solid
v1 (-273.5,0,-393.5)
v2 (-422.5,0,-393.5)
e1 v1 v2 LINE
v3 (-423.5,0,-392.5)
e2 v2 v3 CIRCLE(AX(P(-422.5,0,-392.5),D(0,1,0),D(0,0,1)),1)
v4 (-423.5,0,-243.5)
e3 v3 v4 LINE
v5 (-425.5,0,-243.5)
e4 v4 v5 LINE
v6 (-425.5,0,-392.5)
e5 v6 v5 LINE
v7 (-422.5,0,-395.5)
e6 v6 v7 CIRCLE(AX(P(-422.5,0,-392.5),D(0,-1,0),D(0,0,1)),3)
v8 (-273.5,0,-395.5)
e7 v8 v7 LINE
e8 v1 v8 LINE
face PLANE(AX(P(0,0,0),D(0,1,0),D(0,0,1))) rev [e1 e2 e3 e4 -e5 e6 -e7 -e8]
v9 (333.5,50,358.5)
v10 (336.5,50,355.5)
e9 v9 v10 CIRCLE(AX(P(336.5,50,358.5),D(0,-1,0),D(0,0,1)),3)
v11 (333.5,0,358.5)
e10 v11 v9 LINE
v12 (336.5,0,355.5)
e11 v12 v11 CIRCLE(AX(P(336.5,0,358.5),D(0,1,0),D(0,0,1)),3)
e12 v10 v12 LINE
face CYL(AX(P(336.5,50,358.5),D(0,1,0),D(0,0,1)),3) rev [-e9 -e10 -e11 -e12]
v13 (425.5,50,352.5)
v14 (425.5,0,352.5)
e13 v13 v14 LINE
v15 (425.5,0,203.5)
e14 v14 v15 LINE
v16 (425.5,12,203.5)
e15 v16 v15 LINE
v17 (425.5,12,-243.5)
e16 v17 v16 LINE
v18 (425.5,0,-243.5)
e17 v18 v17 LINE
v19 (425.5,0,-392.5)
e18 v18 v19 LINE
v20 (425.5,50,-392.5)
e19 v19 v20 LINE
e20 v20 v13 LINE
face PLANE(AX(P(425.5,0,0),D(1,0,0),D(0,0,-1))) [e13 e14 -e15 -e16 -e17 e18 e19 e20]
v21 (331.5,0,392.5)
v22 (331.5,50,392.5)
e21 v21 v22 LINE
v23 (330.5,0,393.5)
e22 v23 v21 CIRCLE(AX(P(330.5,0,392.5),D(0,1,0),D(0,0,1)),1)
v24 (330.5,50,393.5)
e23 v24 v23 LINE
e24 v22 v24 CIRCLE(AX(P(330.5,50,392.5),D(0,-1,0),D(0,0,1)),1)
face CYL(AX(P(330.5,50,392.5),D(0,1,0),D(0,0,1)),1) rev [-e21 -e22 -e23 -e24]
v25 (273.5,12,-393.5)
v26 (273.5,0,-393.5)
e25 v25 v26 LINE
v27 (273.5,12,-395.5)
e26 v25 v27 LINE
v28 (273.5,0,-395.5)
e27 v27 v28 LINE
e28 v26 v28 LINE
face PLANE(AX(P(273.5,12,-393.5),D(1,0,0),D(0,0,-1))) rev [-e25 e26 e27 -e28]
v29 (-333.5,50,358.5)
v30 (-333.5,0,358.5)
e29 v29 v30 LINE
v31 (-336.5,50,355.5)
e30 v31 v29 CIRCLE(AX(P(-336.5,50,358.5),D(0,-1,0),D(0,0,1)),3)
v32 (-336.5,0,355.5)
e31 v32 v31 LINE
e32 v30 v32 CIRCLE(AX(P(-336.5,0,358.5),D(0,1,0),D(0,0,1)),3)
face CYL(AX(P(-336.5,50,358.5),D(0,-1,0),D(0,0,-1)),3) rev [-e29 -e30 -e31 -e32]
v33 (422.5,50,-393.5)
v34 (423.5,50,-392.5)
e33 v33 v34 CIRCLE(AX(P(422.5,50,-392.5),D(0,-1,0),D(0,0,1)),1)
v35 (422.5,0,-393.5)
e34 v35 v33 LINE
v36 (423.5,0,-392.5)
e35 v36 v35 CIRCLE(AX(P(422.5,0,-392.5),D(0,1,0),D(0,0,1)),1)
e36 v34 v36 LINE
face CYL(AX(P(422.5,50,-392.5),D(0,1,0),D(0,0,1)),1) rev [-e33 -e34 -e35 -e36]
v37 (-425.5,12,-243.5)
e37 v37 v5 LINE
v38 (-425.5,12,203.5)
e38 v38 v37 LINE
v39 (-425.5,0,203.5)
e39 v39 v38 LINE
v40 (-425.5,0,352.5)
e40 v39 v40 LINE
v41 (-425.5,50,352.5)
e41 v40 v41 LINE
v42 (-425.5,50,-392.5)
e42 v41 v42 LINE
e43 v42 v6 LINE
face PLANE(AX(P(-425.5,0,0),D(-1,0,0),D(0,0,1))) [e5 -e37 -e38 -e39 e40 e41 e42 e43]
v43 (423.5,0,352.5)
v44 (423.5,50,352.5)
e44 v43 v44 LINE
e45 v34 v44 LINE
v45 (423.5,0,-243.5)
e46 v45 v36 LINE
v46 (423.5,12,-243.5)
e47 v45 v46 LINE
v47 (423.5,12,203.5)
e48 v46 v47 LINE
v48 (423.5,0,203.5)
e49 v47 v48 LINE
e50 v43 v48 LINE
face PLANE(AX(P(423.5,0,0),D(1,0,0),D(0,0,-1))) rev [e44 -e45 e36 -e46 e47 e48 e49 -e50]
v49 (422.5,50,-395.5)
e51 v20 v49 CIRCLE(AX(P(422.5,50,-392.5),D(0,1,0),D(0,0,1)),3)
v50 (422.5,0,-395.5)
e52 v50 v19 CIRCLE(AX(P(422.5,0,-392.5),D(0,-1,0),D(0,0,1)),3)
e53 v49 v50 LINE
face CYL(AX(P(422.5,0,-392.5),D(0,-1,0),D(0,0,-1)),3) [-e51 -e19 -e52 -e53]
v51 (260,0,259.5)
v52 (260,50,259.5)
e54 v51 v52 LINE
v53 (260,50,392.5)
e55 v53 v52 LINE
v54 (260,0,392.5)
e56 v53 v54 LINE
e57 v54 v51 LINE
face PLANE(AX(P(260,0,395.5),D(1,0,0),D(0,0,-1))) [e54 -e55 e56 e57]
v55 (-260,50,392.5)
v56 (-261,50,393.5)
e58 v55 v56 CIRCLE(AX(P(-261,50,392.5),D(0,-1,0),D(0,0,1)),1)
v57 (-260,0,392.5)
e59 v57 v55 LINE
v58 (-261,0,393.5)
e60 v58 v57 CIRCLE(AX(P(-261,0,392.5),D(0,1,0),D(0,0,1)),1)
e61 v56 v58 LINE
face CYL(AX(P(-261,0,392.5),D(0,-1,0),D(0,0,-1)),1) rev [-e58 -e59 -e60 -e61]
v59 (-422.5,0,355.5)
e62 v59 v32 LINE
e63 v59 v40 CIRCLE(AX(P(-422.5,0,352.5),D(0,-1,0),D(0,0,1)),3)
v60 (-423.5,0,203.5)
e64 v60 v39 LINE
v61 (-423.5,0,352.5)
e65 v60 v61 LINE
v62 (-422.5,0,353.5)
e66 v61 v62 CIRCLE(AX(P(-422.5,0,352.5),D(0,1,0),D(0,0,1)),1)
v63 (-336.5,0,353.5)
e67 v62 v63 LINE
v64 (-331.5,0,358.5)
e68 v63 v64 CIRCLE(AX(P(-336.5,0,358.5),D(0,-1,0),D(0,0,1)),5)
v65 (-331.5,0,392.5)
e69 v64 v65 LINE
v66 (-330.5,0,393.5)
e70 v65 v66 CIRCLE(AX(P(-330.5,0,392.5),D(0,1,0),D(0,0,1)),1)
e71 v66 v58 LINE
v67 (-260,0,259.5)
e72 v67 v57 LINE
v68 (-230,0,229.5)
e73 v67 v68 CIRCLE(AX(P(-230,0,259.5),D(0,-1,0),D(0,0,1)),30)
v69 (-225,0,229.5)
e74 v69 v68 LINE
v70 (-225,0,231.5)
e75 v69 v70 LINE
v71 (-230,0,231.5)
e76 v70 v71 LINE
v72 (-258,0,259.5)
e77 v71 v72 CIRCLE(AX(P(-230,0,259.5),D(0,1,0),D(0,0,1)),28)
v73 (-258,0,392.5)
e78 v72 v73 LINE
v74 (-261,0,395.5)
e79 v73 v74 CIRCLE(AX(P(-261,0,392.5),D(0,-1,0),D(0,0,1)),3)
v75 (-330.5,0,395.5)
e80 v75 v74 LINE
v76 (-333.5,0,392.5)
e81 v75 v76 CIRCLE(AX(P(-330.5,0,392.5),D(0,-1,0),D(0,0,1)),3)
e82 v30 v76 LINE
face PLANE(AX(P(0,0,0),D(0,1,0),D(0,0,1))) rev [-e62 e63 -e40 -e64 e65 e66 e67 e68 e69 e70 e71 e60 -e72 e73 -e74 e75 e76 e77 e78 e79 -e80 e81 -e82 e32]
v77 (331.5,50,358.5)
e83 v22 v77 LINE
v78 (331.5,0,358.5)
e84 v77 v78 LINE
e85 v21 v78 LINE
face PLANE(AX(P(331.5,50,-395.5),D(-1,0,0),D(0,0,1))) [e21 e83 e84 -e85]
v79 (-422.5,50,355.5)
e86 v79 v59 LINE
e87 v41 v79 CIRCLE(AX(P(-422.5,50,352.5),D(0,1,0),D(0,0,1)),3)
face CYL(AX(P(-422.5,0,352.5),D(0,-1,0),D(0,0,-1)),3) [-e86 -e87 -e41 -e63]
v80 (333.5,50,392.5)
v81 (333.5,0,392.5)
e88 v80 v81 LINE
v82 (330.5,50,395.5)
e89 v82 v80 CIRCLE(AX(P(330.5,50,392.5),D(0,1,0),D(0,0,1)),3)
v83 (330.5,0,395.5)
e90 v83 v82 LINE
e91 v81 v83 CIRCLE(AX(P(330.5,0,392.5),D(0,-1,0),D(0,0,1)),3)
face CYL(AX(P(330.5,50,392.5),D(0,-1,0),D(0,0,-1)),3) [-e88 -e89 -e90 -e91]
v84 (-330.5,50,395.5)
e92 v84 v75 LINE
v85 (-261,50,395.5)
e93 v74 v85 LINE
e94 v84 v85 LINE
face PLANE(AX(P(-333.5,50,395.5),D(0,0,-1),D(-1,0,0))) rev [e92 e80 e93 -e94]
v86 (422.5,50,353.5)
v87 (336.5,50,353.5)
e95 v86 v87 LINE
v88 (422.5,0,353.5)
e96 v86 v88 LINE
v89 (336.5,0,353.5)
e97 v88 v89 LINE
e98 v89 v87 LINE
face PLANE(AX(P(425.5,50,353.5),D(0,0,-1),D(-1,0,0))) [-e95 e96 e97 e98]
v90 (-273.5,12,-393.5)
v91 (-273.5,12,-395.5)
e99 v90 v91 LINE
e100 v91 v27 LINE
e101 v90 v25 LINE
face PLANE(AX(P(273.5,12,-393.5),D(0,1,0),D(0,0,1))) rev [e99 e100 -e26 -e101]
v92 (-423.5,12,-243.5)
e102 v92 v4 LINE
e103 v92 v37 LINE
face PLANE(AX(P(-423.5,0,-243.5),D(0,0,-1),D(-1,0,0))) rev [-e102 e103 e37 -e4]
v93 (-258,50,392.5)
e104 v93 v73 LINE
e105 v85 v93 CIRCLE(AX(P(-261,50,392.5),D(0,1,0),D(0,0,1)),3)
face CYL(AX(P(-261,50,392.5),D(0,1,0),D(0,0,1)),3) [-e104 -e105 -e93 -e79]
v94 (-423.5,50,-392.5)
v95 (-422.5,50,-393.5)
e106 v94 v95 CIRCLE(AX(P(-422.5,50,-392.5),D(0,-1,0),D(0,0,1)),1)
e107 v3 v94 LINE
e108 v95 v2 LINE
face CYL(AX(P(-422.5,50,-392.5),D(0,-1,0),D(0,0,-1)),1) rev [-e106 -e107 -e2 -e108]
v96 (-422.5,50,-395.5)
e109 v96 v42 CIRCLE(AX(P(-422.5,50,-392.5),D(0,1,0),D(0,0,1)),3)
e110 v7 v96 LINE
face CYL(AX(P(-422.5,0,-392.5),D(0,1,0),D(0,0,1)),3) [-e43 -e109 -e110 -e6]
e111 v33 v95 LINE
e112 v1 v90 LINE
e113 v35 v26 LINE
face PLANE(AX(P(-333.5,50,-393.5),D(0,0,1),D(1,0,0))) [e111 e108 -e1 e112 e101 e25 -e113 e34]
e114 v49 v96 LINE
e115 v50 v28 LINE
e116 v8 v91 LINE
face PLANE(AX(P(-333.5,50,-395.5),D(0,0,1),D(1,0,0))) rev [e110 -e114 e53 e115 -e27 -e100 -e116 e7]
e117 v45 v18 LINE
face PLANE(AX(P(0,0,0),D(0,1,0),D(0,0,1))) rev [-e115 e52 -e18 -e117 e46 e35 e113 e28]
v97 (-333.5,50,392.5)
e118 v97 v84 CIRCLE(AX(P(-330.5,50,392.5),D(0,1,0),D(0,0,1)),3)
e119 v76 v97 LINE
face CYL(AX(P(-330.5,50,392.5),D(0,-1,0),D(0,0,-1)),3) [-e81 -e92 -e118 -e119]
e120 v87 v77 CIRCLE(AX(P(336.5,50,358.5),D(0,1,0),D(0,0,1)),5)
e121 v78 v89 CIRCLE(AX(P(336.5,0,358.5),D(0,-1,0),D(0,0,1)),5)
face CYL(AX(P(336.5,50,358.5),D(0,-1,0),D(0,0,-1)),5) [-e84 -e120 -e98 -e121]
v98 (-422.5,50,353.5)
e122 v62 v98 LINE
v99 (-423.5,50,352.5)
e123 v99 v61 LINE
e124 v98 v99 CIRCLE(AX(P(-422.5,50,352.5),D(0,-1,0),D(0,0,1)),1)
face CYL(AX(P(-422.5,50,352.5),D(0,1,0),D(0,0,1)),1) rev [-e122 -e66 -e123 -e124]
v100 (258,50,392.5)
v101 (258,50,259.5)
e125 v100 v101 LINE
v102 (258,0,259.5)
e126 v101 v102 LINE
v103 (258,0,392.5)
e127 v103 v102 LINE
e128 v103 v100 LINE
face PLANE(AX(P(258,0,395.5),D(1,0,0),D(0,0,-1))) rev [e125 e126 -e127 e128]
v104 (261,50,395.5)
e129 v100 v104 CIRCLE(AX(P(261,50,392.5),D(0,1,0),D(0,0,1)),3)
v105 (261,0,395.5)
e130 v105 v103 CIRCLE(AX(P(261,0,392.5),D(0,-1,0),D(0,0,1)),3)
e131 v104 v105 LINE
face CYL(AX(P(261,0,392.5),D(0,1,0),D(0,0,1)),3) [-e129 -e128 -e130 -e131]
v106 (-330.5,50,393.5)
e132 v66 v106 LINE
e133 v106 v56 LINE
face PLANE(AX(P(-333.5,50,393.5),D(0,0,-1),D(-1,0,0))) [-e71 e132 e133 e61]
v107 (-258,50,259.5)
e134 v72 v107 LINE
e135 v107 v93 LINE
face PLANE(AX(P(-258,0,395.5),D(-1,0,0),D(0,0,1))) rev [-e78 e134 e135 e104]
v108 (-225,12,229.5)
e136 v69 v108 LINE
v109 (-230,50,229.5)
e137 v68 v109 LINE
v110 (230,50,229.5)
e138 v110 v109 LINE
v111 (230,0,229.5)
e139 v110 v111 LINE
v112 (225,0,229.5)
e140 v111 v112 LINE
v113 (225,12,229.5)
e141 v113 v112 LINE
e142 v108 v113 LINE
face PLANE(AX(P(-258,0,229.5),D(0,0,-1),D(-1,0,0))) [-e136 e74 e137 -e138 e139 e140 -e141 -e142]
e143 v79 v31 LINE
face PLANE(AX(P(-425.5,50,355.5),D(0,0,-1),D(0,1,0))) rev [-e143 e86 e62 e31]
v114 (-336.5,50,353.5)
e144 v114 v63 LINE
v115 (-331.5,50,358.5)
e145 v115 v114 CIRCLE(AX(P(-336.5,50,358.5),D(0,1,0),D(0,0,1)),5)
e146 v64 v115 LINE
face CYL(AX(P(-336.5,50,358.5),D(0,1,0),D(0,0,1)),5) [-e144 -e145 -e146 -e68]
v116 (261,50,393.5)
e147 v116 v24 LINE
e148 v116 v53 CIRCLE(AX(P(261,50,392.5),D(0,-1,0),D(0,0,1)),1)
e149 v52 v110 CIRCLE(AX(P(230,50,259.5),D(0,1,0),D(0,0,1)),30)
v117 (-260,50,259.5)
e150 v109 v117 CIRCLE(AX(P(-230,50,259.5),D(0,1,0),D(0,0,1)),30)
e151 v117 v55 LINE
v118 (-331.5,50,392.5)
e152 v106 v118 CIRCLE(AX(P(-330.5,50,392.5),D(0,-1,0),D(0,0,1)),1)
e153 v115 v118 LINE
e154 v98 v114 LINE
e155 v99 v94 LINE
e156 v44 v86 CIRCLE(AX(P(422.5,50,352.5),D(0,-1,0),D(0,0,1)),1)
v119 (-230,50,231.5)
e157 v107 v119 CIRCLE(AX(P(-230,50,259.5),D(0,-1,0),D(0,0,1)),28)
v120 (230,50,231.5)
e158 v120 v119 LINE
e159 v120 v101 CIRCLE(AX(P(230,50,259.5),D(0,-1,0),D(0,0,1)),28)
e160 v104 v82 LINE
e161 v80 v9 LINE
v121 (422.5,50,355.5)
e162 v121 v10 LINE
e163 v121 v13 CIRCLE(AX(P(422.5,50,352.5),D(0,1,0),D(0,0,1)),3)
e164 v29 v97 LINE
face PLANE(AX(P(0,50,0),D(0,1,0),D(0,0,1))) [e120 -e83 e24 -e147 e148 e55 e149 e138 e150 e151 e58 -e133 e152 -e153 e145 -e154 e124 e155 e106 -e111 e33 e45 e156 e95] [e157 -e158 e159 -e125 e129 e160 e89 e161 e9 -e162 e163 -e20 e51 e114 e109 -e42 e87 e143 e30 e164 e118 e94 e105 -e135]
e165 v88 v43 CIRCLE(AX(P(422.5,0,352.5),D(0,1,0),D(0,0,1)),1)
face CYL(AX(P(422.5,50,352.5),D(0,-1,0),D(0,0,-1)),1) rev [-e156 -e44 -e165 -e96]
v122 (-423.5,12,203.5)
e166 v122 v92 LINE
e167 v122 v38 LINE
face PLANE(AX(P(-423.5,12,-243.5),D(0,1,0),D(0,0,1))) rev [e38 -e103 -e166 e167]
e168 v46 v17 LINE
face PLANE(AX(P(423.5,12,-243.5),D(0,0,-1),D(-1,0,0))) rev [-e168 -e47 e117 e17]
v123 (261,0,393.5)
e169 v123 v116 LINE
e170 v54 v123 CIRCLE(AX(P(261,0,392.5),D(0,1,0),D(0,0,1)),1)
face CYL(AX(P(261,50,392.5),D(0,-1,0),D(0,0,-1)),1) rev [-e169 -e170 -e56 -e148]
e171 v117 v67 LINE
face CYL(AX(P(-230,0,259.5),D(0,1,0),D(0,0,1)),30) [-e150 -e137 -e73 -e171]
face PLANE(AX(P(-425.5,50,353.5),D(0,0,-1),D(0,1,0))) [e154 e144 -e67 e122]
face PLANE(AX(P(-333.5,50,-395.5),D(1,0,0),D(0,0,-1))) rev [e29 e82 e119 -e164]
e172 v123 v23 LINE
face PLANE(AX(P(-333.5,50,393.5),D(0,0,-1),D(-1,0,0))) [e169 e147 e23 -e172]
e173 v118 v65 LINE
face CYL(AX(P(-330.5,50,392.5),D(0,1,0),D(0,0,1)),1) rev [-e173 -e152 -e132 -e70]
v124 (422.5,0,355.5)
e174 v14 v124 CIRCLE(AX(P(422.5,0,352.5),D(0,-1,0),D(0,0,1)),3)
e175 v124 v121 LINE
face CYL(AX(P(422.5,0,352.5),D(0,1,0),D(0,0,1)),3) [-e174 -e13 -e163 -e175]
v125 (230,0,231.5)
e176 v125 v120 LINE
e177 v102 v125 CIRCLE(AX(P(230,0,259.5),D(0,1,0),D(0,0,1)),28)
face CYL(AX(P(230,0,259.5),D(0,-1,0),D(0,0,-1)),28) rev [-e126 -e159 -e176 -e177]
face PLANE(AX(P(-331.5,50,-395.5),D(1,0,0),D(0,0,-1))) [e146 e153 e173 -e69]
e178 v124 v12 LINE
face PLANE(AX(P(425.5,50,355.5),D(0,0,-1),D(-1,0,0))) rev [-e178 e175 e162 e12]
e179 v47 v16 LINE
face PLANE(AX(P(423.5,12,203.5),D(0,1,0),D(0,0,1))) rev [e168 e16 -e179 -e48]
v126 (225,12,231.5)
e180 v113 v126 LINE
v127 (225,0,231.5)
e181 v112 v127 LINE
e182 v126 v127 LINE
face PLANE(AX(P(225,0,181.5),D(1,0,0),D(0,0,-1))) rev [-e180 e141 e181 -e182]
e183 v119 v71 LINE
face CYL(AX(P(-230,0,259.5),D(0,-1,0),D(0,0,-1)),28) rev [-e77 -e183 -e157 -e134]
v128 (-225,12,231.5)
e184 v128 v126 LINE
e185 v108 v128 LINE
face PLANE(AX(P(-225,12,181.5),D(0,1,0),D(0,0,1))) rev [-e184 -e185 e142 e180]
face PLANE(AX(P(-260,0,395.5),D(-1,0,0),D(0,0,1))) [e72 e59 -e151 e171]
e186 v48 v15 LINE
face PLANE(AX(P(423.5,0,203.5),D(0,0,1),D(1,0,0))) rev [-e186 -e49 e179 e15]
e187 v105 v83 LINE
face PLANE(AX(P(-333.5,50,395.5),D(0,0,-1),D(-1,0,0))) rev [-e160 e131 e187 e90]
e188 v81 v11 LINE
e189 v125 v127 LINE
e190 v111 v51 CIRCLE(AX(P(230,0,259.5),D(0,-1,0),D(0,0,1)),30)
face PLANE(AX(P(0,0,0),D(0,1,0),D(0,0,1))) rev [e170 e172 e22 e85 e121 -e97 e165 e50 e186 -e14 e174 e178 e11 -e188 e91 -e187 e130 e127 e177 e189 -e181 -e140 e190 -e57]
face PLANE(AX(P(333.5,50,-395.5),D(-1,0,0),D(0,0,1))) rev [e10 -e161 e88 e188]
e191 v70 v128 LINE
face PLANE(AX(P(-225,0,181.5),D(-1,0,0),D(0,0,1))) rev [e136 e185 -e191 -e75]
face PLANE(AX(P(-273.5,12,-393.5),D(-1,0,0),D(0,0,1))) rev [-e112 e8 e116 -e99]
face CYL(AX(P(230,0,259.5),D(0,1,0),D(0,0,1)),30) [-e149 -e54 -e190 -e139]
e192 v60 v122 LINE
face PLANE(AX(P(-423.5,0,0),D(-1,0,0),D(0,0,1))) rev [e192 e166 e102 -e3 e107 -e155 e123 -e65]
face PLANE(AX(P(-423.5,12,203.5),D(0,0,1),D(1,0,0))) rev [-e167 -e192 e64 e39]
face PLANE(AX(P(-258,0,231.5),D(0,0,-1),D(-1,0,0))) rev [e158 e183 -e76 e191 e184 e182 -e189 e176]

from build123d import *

# Parameters (mm, degrees)
SKETCH_1_W          = 667
SKETCH_1_H          = 791
EXTRUDE_1_DEPTH     = 50
SKETCH_6_W          = 516
SKETCH_6_H          = 164
CUT_EXTRUDE_1_DEPTH = 520.752344872
SKETCH_4_W          = 751
SKETCH_4_H          = 50
EXTRUDE_2_DEPTH     = 92
SKETCH_5_W          = 751
SKETCH_5_H          = 50
EXTRUDE_3_DEPTH     = 92
SHELL_2_T           = -2
FILLET_1_R          = 1
FILLET_2_R          = 3
FILLET_3_R          = 5
FILLET_4_R          = 28
FILLET_5_R          = 30
SKETCH_7_W          = 447
SKETCH_7_H          = 12
CUT_EXTRUDE_2_DEPTH = 2
SKETCH_8_W          = 447
SKETCH_8_H          = 12
CUT_EXTRUDE_3_DEPTH = 2
SKETCH_9_W          = 547
SKETCH_9_H          = 12
CUT_EXTRUDE_4_DEPTH = 2
SKETCH_10_W         = 450
SKETCH_10_H         = 12
CUT_EXTRUDE_5_DEPTH = 50


with BuildPart() as part:
    # 草图1 → 凸台-拉伸1 (new body)
    with BuildSketch(Plane(origin=(0, 0, 0), x_dir=(1, 0, 0), z_dir=(0, 1, 0))):
        Rectangle(SKETCH_1_W, SKETCH_1_H)
    extrude(amount=EXTRUDE_1_DEPTH)

    # 草图6 → 切除-拉伸1 (cut, through all)
    with BuildSketch(Plane(origin=(0, 50, 0), x_dir=(1, 0, 0), z_dir=(0, 1, 0))):
        with Locations((0, -313.5)):
            Rectangle(SKETCH_6_W, SKETCH_6_H)
    extrude(amount=-CUT_EXTRUDE_1_DEPTH, mode=Mode.SUBTRACT)

    # 草图4 → 凸台-拉伸2 (add)
    with BuildSketch(Plane(origin=(333.5, 0, 0), x_dir=(0, 0, -1), z_dir=(1, 0, 0))):
        with Locations((20, 25)):
            Rectangle(SKETCH_4_W, SKETCH_4_H)
    extrude(amount=EXTRUDE_2_DEPTH)

    # 草图5 → 凸台-拉伸3 (add)
    with BuildSketch(Plane.ZY.offset(333.5)):
        with Locations((-20, 25)):
            Rectangle(SKETCH_5_W, SKETCH_5_H)
    extrude(amount=EXTRUDE_3_DEPTH)

    # 抽壳2
    shell_2_openings = [part.faces().sort_by_distance(p)[0] for p in [
        (0, 50, -50.405146974),
        (0, 0, -50.405146974),
    ]]
    offset(amount=SHELL_2_T, openings=shell_2_openings, kind=Kind.INTERSECTION)

    # 圆角1
    fillet_1_edges = [part.edges().sort_by_distance(p)[0] for p in [
        (331.5, 25, 393.5),
        (-260, 25, 393.5),
        (-331.5, 25, 393.5),
        (260, 25, 393.5),
        (423.5, 25, 353.5),
        (423.5, 25, -393.5),
        (-423.5, 25, -393.5),
        (-423.5, 25, 353.5),
    ]]
    fillet(fillet_1_edges, radius=FILLET_1_R)

    # 圆角2
    fillet_2_edges = [part.edges().sort_by_distance(p)[0] for p in [
        (-333.5, 25, 355.5),
        (333.5, 25, 355.5),
        (425.5, 25, 355.5),
        (425.5, 25, -395.5),
        (-425.5, 25, -395.5),
        (-425.5, 25, 355.5),
        (333.5, 25, 395.5),
        (-333.5, 25, 395.5),
        (258, 25, 395.5),
        (-258, 25, 395.5),
    ]]
    fillet(fillet_2_edges, radius=FILLET_2_R)

    # 圆角3
    fillet_3_edges = [part.edges().sort_by_distance(p)[0] for p in [
        (331.5, 25, 353.5),
        (-331.5, 25, 353.5),
    ]]
    fillet(fillet_3_edges, radius=FILLET_3_R)

    # 圆角4
    fillet_4_edges = [part.edges().sort_by_distance(p)[0] for p in [
        (-258, 25, 231.5),
        (258, 25, 231.5),
    ]]
    fillet(fillet_4_edges, radius=FILLET_4_R)

    # 圆角5
    fillet_5_edges = [part.edges().sort_by_distance(p)[0] for p in [
        (-260, 25, 229.5),
        (260, 25, 229.5),
    ]]
    fillet(fillet_5_edges, radius=FILLET_5_R)

    # 草图7 → 切除-拉伸2 (cut)
    with BuildSketch(Plane(origin=(425.5, 0, 0), x_dir=(0, 0, -1), z_dir=(1, 0, 0))):
        with Locations((20, 6)):
            Rectangle(SKETCH_7_W, SKETCH_7_H)
    extrude(amount=-CUT_EXTRUDE_2_DEPTH, mode=Mode.SUBTRACT)

    # 草图8 → 切除-拉伸3 (cut)
    with BuildSketch(Plane.ZY.offset(425.5)):
        with Locations((-20, 6)):
            Rectangle(SKETCH_8_W, SKETCH_8_H)
    extrude(amount=-CUT_EXTRUDE_3_DEPTH, mode=Mode.SUBTRACT)

    # 草图9 → 切除-拉伸4 (cut)
    with BuildSketch(Plane(origin=(0, 0, -395.5), x_dir=(-1, 0, 0), z_dir=(0, 0, -1))):
        with Locations((0, 6)):
            Rectangle(SKETCH_9_W, SKETCH_9_H)
    extrude(amount=-CUT_EXTRUDE_4_DEPTH, mode=Mode.SUBTRACT)

    # 草图10 → 切除-拉伸5 (cut, symmetric)
    with BuildSketch(Plane.XY.offset(231.5)):
        with Locations((0, 6)):
            Rectangle(SKETCH_10_W, SKETCH_10_H)
    extrude(amount=CUT_EXTRUDE_5_DEPTH, both=True, mode=Mode.SUBTRACT)


solid = part.part
